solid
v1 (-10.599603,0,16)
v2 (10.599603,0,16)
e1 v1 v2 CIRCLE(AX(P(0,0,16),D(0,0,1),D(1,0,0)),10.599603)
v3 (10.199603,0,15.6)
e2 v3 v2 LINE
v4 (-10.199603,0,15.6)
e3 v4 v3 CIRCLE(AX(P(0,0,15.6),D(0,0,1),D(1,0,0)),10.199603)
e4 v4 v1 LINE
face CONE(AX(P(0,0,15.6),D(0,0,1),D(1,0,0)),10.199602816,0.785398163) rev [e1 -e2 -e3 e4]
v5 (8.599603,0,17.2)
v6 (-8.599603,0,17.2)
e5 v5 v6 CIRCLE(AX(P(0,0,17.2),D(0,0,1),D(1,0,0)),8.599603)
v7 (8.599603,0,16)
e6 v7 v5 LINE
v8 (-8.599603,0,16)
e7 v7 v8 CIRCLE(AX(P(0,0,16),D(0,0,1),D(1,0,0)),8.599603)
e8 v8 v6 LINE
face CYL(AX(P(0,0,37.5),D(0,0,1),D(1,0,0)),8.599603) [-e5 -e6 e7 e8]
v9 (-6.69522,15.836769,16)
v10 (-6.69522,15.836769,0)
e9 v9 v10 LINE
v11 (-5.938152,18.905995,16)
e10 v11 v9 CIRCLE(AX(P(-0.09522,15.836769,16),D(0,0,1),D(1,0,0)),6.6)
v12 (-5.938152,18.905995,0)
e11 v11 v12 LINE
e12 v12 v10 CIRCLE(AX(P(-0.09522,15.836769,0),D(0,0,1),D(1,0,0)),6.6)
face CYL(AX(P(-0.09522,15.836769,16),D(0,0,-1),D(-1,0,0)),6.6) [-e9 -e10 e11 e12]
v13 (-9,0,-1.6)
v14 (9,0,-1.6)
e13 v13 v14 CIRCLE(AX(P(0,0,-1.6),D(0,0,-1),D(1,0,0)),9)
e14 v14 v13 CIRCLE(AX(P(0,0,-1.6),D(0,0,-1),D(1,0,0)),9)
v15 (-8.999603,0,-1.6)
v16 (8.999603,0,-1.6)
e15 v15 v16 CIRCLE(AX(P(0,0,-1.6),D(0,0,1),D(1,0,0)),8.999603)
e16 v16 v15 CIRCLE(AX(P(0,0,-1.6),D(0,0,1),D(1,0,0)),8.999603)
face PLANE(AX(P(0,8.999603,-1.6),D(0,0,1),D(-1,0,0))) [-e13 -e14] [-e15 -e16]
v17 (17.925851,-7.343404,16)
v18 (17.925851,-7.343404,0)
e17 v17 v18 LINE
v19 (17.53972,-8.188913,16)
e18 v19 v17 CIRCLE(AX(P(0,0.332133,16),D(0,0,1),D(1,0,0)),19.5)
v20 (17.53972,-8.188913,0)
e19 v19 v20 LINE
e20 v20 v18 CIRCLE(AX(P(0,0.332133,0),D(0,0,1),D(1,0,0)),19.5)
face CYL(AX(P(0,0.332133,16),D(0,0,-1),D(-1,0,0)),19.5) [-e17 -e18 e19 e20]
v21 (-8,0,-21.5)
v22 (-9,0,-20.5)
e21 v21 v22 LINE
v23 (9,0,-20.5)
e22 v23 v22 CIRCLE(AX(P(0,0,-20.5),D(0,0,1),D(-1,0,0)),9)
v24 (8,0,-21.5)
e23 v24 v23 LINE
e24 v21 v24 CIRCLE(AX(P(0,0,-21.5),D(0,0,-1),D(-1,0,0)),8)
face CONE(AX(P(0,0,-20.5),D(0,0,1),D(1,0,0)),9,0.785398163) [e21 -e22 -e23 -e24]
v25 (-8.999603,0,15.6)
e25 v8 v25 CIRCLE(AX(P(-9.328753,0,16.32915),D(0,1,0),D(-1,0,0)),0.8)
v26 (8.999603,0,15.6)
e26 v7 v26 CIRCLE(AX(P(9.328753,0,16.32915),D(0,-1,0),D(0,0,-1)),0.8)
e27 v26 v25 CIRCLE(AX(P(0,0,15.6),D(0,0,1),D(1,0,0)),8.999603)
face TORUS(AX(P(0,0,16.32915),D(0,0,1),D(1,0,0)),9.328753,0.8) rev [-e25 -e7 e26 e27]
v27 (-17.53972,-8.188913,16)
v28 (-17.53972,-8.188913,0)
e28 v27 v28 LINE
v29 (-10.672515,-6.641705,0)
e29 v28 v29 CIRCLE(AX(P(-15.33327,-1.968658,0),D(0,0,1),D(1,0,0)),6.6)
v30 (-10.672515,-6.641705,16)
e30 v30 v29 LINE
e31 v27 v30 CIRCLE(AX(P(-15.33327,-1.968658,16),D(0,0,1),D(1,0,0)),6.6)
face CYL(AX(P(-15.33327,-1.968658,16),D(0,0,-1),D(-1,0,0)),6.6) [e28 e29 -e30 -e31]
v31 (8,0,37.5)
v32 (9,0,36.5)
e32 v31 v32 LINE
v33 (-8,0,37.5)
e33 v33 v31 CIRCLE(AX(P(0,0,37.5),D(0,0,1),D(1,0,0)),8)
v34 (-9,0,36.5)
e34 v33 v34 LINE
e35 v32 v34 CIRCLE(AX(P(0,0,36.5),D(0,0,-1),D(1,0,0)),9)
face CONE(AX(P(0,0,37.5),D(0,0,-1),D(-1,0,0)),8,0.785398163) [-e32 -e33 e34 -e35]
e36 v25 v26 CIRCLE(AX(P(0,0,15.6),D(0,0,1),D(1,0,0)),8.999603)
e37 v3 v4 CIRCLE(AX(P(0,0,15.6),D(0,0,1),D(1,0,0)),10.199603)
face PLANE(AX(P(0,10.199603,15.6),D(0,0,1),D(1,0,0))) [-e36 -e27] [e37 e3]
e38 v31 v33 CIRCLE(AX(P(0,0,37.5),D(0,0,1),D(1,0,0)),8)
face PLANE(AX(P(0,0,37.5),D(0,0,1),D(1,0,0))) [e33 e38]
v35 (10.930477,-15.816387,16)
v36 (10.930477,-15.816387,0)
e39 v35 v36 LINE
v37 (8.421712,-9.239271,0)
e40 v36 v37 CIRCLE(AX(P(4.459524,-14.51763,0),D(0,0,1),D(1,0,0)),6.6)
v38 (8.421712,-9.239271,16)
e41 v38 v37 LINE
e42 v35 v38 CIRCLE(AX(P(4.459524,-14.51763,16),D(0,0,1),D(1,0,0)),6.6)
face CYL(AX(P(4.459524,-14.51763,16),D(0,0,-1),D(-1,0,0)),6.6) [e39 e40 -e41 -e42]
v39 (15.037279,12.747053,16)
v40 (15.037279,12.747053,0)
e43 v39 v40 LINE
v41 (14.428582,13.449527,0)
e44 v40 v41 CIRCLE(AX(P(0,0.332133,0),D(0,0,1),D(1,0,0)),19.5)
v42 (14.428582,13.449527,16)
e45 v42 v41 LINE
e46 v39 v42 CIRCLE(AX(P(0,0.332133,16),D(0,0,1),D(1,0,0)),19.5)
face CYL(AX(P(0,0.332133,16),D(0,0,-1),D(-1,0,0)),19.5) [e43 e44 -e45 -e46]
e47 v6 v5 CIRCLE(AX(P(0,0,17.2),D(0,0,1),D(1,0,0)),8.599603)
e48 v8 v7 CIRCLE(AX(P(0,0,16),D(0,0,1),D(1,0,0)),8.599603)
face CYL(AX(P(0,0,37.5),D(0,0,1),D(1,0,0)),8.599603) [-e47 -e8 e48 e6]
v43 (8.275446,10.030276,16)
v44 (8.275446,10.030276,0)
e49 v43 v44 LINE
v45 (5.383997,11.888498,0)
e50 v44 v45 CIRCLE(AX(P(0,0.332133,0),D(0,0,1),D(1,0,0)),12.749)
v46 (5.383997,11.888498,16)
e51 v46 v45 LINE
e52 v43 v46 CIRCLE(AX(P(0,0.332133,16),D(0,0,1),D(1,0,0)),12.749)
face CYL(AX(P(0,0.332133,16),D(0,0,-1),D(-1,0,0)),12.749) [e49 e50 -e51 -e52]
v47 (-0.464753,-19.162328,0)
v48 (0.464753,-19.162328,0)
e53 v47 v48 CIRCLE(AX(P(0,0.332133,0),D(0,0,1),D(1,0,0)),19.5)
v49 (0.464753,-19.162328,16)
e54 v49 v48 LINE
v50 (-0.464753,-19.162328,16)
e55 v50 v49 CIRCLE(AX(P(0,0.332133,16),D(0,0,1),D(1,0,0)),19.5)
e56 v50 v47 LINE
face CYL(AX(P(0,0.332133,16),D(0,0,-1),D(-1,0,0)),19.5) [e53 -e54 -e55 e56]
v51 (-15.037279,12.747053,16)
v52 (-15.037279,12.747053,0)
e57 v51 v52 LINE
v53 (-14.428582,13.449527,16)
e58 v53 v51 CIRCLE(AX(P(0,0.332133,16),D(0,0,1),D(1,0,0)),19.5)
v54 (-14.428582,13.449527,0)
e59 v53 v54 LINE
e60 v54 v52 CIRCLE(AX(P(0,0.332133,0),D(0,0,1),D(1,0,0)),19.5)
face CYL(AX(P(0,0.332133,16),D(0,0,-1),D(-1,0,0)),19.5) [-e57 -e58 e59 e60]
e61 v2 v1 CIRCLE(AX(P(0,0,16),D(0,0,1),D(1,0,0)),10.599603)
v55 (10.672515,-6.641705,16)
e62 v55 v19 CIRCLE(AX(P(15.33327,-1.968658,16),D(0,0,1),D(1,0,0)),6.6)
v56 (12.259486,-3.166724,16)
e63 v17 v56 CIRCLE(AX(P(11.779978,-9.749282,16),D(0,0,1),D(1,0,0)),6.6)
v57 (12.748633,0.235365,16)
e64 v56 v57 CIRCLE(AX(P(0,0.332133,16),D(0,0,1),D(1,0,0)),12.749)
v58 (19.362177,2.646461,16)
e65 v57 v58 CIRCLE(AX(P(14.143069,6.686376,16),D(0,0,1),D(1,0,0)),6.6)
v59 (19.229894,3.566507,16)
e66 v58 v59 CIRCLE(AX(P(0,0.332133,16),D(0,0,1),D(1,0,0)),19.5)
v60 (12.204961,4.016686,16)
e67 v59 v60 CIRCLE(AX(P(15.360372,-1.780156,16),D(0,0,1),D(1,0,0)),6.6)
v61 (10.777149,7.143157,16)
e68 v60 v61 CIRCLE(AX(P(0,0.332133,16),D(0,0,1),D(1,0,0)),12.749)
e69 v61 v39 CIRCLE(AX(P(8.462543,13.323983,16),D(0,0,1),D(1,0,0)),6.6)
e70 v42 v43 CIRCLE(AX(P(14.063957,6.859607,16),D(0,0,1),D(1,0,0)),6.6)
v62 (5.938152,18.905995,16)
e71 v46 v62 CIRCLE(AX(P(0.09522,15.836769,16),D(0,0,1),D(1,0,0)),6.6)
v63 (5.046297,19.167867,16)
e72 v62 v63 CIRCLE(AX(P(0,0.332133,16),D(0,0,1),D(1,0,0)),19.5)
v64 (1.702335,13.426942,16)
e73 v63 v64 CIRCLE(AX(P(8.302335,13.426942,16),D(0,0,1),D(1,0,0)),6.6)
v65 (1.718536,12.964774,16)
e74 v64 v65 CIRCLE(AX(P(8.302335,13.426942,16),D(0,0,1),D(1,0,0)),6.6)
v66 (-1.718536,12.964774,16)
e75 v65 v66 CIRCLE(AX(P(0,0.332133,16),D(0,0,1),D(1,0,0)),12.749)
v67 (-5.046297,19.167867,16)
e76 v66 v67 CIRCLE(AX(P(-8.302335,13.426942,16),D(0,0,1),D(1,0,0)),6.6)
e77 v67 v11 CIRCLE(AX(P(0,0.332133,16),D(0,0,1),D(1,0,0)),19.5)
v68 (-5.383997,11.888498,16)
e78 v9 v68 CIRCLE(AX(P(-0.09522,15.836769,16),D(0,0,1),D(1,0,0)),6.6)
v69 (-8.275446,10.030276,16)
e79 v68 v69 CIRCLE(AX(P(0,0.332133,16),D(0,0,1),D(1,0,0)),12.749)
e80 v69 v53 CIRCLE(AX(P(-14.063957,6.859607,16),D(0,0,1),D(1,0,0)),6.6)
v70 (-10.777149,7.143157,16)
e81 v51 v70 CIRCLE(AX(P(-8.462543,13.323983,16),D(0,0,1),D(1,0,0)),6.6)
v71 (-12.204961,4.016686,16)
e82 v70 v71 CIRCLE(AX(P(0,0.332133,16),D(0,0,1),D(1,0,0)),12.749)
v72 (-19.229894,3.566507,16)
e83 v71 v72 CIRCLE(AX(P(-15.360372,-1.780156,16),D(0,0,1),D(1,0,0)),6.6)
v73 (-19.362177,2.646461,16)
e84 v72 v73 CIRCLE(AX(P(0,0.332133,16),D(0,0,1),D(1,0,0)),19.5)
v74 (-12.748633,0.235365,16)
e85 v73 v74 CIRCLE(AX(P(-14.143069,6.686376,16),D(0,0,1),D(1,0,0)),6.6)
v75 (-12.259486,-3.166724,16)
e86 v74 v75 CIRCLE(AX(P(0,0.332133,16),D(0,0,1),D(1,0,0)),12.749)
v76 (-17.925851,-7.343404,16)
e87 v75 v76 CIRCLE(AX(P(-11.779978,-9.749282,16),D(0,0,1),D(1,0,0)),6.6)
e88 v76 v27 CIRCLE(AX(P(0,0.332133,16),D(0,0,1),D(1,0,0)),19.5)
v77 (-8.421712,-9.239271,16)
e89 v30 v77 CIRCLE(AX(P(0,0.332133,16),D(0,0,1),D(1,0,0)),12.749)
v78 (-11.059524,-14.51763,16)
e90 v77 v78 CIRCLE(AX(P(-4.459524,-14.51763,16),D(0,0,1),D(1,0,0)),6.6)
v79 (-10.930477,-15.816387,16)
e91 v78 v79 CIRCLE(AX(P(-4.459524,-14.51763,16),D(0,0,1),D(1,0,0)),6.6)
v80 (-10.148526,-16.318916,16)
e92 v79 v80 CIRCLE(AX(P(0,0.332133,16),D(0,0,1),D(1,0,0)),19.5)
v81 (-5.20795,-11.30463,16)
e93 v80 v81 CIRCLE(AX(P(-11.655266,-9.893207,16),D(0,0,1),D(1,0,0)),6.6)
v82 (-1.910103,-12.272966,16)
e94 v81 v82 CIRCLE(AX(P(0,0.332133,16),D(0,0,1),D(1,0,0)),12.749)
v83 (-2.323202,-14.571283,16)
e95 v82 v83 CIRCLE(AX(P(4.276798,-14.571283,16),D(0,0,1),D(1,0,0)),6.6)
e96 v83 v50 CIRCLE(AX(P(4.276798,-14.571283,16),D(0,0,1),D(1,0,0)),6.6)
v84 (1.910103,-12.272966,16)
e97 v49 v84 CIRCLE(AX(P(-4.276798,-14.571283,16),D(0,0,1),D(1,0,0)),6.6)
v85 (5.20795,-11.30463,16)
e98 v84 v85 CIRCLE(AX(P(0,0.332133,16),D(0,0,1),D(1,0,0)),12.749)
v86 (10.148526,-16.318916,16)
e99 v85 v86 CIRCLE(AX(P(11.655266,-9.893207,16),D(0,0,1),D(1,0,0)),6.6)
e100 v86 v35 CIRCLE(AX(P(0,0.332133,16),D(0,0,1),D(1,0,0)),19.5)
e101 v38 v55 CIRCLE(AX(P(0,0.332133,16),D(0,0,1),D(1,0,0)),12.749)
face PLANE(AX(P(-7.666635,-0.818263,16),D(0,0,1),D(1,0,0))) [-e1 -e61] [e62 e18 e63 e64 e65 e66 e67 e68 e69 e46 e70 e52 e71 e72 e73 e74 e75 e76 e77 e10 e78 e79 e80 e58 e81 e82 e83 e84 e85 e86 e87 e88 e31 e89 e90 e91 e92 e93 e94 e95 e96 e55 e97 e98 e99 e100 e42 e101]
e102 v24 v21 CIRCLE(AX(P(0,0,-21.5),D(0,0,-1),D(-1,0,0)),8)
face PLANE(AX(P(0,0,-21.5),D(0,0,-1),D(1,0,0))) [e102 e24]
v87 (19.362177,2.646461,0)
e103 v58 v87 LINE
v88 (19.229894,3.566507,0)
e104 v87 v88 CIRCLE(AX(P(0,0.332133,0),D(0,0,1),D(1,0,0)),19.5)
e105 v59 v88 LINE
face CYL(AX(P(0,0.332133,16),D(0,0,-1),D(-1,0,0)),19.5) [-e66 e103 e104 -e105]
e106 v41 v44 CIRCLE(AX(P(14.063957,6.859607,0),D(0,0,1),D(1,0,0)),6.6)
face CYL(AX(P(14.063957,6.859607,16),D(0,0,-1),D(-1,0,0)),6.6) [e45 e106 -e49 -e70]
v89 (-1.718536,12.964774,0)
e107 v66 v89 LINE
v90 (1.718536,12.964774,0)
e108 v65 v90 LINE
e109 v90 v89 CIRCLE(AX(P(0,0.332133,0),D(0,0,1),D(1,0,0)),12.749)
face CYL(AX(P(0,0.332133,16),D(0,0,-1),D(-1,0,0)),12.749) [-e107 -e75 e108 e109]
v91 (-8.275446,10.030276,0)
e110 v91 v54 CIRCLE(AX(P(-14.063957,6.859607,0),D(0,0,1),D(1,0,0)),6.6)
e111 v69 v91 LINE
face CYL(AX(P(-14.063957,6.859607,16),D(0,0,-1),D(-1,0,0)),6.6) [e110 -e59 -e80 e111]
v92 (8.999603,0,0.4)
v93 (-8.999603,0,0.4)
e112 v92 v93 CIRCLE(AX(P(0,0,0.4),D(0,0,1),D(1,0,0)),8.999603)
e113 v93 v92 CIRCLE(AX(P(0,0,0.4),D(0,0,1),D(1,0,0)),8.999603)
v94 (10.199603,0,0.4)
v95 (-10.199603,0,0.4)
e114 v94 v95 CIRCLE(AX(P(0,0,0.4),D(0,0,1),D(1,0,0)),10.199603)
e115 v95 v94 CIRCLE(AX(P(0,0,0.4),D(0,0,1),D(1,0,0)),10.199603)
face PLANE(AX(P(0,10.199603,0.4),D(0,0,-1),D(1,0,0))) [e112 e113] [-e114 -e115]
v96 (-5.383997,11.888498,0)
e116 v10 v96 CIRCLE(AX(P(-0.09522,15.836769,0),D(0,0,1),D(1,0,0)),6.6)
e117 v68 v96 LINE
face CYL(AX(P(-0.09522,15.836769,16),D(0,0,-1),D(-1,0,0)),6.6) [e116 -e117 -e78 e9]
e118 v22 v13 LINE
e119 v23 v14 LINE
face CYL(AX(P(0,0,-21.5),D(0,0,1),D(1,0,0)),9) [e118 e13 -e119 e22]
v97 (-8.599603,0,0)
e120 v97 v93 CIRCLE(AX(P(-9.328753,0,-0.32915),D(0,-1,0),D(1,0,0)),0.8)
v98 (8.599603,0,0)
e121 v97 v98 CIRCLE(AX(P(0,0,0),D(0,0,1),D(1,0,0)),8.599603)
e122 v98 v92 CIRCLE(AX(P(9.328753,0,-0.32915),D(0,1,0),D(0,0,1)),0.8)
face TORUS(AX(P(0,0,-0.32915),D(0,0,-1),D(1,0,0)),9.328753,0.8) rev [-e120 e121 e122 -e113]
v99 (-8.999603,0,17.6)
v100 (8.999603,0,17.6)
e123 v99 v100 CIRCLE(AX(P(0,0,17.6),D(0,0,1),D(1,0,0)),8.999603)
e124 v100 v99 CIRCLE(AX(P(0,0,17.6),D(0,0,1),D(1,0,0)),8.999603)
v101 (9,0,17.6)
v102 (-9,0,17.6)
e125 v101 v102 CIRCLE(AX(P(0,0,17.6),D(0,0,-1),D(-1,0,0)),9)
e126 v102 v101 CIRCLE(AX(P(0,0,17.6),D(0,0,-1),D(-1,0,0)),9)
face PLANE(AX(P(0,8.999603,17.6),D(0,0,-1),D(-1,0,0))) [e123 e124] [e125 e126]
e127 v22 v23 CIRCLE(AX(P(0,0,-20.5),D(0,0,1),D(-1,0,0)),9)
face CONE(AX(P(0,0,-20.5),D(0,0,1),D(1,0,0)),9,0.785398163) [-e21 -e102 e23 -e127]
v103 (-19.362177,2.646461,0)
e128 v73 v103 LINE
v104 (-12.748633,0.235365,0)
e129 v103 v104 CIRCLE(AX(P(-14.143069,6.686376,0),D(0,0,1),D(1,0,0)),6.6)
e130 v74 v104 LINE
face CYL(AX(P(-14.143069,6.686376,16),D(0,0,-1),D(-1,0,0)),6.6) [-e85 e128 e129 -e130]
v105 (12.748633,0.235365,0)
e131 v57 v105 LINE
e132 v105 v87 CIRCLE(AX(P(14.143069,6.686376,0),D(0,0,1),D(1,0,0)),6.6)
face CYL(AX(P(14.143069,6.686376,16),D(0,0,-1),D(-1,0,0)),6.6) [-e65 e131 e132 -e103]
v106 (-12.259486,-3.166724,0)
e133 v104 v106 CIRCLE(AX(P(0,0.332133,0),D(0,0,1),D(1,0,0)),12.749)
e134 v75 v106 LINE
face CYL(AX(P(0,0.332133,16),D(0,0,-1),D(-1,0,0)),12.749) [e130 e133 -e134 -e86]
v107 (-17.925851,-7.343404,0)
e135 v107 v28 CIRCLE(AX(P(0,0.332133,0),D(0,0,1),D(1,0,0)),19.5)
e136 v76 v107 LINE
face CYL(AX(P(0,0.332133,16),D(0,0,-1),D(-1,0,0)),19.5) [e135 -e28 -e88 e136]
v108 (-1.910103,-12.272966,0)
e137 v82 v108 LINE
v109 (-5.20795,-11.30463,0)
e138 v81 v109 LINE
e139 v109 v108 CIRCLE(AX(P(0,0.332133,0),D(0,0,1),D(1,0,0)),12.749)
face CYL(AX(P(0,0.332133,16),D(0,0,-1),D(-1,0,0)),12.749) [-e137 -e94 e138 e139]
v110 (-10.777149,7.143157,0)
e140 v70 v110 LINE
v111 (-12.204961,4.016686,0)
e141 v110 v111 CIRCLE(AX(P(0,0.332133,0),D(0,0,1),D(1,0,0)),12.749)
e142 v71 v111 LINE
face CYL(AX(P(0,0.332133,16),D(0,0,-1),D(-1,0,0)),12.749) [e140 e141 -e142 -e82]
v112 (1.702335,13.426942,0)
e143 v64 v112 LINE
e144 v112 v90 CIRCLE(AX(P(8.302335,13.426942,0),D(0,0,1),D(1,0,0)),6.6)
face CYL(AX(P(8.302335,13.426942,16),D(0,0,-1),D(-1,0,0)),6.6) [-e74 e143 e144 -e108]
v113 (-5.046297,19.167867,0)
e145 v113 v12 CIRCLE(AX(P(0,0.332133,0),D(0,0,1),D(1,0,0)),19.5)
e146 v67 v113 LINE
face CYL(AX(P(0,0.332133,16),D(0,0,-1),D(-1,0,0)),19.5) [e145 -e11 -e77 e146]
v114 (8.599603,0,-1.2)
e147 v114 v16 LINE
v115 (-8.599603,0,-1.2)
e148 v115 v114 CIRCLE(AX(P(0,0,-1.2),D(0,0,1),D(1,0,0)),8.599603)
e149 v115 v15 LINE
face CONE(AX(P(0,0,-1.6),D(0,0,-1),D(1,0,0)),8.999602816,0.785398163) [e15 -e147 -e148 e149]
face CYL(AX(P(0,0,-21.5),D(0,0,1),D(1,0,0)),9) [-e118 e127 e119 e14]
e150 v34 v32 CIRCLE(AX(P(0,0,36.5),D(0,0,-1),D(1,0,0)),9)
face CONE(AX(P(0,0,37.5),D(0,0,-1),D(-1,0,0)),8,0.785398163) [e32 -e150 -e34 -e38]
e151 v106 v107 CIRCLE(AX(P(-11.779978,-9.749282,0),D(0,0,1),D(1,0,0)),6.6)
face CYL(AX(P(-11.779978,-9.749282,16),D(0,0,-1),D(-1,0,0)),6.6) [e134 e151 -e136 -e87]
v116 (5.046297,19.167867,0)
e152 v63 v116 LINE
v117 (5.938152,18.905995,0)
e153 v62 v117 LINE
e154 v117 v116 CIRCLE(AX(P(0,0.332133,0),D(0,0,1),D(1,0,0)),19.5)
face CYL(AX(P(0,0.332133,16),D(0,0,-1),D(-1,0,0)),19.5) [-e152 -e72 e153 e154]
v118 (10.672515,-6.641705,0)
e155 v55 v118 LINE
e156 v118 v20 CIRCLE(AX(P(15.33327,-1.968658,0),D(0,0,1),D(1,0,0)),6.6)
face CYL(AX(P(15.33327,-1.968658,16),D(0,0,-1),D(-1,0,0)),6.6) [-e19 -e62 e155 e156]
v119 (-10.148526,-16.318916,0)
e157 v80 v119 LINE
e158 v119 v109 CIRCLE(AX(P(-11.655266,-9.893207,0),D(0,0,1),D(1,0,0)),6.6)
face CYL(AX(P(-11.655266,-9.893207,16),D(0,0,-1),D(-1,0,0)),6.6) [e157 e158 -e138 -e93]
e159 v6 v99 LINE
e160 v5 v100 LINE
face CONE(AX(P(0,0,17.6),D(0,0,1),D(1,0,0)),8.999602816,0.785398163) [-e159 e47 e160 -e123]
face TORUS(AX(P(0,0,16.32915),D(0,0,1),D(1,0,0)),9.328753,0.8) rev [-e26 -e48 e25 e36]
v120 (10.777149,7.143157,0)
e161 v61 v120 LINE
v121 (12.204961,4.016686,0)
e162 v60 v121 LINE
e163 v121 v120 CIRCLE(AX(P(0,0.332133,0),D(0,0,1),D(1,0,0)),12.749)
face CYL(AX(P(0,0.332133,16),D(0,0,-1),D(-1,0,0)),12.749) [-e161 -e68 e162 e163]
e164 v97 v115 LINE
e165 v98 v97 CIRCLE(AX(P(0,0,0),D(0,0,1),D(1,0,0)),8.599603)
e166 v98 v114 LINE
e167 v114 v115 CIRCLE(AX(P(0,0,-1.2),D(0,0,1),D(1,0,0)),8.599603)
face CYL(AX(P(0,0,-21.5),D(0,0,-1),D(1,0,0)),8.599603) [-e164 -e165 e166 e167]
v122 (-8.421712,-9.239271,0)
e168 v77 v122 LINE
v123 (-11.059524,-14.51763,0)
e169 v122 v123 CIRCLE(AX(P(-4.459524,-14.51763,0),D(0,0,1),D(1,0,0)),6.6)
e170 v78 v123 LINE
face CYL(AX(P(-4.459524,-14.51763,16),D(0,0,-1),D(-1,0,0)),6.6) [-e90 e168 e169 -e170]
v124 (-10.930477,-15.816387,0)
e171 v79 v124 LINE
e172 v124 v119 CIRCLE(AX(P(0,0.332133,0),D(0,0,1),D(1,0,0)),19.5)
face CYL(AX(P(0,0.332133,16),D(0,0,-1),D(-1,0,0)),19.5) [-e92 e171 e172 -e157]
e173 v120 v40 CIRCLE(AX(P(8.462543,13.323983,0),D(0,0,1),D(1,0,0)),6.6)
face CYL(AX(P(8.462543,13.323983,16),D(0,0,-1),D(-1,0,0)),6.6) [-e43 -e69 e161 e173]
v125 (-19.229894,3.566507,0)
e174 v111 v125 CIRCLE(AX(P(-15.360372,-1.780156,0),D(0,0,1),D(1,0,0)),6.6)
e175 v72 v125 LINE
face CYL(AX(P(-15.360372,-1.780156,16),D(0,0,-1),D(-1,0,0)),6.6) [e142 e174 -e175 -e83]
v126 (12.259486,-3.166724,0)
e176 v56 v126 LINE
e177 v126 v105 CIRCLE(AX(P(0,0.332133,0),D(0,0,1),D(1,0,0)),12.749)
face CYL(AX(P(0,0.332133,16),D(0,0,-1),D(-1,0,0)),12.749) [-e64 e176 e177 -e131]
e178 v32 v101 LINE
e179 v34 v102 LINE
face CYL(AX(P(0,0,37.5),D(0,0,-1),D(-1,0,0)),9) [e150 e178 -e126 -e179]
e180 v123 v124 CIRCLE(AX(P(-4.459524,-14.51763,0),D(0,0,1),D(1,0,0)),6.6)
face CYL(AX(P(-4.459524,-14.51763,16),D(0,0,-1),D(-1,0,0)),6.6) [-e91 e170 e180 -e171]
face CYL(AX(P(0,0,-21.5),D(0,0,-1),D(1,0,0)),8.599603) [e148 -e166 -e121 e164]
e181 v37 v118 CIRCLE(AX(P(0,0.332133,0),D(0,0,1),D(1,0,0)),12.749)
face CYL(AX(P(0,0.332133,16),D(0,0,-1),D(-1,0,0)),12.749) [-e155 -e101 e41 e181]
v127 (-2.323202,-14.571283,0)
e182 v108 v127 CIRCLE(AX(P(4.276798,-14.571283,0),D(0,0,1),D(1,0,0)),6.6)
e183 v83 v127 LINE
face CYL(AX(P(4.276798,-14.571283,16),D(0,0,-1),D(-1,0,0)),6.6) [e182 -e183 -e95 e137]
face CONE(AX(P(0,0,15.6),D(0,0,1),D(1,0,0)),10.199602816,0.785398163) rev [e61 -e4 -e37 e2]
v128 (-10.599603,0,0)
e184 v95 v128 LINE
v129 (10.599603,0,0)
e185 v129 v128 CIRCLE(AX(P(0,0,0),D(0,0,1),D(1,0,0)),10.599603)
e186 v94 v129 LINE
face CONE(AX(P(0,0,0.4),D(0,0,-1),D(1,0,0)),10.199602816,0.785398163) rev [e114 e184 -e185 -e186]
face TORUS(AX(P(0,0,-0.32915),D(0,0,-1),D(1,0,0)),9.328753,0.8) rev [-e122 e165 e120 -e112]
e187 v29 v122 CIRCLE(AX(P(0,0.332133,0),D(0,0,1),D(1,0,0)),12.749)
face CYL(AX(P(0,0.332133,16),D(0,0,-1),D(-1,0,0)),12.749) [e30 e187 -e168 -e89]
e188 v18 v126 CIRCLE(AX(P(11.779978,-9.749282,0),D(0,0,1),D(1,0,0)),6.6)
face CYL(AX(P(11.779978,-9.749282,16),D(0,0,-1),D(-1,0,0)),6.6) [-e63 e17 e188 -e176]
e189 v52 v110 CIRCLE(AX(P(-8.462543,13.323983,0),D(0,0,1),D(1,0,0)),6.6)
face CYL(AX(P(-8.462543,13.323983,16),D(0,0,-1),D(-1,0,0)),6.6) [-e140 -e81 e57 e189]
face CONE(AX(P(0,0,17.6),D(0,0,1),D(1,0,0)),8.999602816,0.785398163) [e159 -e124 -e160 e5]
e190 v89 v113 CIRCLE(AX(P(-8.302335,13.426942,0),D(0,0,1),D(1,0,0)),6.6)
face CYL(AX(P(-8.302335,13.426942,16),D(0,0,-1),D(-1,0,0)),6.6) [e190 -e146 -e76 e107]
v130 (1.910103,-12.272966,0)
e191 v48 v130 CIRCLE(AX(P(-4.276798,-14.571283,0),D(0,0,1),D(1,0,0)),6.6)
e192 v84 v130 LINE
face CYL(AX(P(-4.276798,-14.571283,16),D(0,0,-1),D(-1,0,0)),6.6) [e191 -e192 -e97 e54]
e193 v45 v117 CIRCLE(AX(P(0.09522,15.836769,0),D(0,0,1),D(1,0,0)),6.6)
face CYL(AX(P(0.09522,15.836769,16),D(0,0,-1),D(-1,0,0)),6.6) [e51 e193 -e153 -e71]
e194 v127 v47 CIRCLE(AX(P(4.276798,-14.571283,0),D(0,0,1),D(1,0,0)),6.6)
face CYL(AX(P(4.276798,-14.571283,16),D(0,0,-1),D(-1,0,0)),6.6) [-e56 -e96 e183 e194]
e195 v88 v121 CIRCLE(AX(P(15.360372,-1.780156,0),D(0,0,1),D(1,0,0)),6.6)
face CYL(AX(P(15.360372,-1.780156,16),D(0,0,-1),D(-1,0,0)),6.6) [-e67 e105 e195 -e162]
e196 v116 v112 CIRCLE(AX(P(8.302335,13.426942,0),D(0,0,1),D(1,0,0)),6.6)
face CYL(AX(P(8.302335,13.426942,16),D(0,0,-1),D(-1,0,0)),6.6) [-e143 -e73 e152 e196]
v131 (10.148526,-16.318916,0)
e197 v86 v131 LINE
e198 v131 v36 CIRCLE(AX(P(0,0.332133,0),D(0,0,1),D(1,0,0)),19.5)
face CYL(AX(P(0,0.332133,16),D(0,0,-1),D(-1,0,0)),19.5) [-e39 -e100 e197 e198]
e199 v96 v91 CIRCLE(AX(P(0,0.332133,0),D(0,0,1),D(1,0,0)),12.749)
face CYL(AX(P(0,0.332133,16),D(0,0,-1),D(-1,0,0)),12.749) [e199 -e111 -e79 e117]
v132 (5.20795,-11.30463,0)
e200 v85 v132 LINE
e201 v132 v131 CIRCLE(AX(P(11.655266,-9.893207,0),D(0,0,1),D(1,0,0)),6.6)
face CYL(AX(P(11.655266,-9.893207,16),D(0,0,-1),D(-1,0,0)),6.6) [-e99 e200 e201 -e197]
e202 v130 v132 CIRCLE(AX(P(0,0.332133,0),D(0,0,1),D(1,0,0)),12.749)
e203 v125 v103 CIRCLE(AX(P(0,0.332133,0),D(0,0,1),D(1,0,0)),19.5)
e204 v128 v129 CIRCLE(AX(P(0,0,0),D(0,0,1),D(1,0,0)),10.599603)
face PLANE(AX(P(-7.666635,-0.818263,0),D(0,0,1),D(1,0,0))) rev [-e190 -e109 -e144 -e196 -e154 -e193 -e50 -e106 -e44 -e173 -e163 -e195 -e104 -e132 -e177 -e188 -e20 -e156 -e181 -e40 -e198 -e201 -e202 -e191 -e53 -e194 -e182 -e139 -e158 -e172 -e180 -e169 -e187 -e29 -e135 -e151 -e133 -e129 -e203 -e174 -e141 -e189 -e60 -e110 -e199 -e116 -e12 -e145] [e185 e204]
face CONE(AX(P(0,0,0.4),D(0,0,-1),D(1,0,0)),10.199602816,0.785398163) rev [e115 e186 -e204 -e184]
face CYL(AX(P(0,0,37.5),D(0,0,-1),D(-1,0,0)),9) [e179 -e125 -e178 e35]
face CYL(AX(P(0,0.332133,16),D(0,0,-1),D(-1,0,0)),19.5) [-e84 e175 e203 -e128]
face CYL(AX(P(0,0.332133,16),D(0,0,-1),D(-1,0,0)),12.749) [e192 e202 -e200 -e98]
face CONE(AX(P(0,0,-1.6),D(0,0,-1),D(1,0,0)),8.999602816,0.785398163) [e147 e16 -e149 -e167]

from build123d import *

# Parameters (mm, degrees)
EXTRUDE_1_DEPTH = 16
SKETCH_3_R      = 9
EXTRUDE_2_DEPTH = 21.5
CHAMFER_1_SIZE  = 1


with BuildPart() as part:
    # 草图2 → 凸台-拉伸1 (new body)
    with BuildSketch(Plane.XY):
        with BuildLine():
            ThreePointArc((-17.539719795, -8.188913461), (-13.882626521, -8.407262966), (-10.672515451, -6.641705083))
            ThreePointArc((-10.672515451, -6.641705083), (-9.635051323, -8.016686689), (-8.421711588, -9.239271212))
            ThreePointArc((-8.421711588, -9.239271212), (-10.626145075, -12.165442895), (-10.930476691, -15.816386607))
            ThreePointArc((-10.930476691, -15.816386607), (-10.54249594, -16.072311082), (-10.148525822, -16.318915917))
            ThreePointArc((-10.148525822, -16.318915917), (-6.95393453, -14.525429313), (-5.207949909, -11.304630433))
            ThreePointArc((-5.207949909, -11.304630433), (-3.591808367, -11.900443112), (-1.910102932, -12.272965675))
            ThreePointArc((-1.910102932, -12.272965675), (-2.18258254, -15.926424664), (-0.464753394, -19.162328053))
            ThreePointArc((-0.464753394, -19.162328053), (0, -19.167867192), (0.464753394, -19.162328053))
            ThreePointArc((0.464753394, -19.162328053), (2.18258254, -15.926424664), (1.910102932, -12.272965675))
            ThreePointArc((1.910102932, -12.272965675), (3.591808367, -11.900443112), (5.207949909, -11.304630433))
            ThreePointArc((5.207949909, -11.304630433), (6.95393453, -14.525429313), (10.148525822, -16.318915917))
            ThreePointArc((10.148525822, -16.318915917), (10.54249594, -16.072311082), (10.930476691, -15.816386607))
            ThreePointArc((10.930476691, -15.816386607), (10.626145075, -12.165442895), (8.421711588, -9.239271212))
            ThreePointArc((8.421711588, -9.239271212), (9.635051323, -8.016686689), (10.672515451, -6.641705083))
            ThreePointArc((10.672515451, -6.641705083), (13.882626521, -8.407262966), (17.539719795, -8.188913461))
            ThreePointArc((17.539719795, -8.188913461), (17.737823909, -7.768459945), (17.925850869, -7.343404347))
            ThreePointArc((17.925850869, -7.343404347), (15.69598163, -4.436569144), (12.25948632, -3.166723601))
            ThreePointArc((12.25948632, -3.166723601), (12.619233563, -1.482239065), (12.748632746, 0.235364522))
            ThreePointArc((12.748632746, 0.235364522), (16.403682682, 0.485599789), (19.362176663, 2.646460979))
            ThreePointArc((19.362176663, 2.646460979), (19.301518117, 3.107272155), (19.229894055, 3.566506728))
            ThreePointArc((19.229894055, 3.566506728), (15.782454919, 4.806333783), (12.204960767, 4.016686199))
            ThreePointArc((12.204960767, 4.016686199), (11.596898309, 5.628258809), (10.777149222, 7.143157375))
            ThreePointArc((10.777149222, 7.143157375), (13.716685494, 9.329737862), (15.037279247, 12.747052577))
            ThreePointArc((15.037279247, 12.747052577), (14.7371167, 13.10191712), (14.42858175, 13.449526936))
            ThreePointArc((14.42858175, 13.449526936), (10.858110285, 12.628709513), (8.275446406, 10.030276331))
            ThreePointArc((8.275446406, 10.030276331), (6.892629782, 11.057274099), (5.383996967, 11.888498053))
            ThreePointArc((5.383996967, 11.888498053), (6.674737579, 15.317199905), (5.938151919, 18.905994868))
            ThreePointArc((5.938151919, 18.905994868), (5.493784858, 19.042245794), (5.046296687, 19.167867192))
            ThreePointArc((5.046296687, 19.167867192), (2.486392356, 16.547009024), (1.718536283, 12.964774418))
            ThreePointArc((1.718536283, 12.964774418), (0, 13.081132808), (-1.718536283, 12.964774418))
            ThreePointArc((-1.718536283, 12.964774418), (-2.486392356, 16.547009024), (-5.046296687, 19.167867192))
            ThreePointArc((-5.046296687, 19.167867192), (-5.493784858, 19.042245794), (-5.938151919, 18.905994868))
            ThreePointArc((-5.938151919, 18.905994868), (-6.674737579, 15.317199905), (-5.383996967, 11.888498053))
            ThreePointArc((-5.383996967, 11.888498053), (-6.892629782, 11.057274099), (-8.275446406, 10.030276331))
            ThreePointArc((-8.275446406, 10.030276331), (-10.858110285, 12.628709513), (-14.42858175, 13.449526936))
            ThreePointArc((-14.42858175, 13.449526936), (-14.7371167, 13.10191712), (-15.037279247, 12.747052577))
            ThreePointArc((-15.037279247, 12.747052577), (-13.716685494, 9.329737862), (-10.777149222, 7.143157375))
            ThreePointArc((-10.777149222, 7.143157375), (-11.596898309, 5.628258809), (-12.204960767, 4.016686199))
            ThreePointArc((-12.204960767, 4.016686199), (-15.782454919, 4.806333783), (-19.229894055, 3.566506728))
            ThreePointArc((-19.229894055, 3.566506728), (-19.301518117, 3.107272155), (-19.362176663, 2.646460979))
            ThreePointArc((-19.362176663, 2.646460979), (-16.403682682, 0.485599789), (-12.748632746, 0.235364522))
            ThreePointArc((-12.748632746, 0.235364522), (-12.619233563, -1.482239065), (-12.25948632, -3.166723601))
            ThreePointArc((-12.25948632, -3.166723601), (-15.69598163, -4.436569144), (-17.925850869, -7.343404347))
            ThreePointArc((-17.925850869, -7.343404347), (-17.737823909, -7.768459945), (-17.539719795, -8.188913461))
        make_face()
    extrude(amount=EXTRUDE_1_DEPTH)

    # 草图3 → 凸台-拉伸2 (add)
    with BuildSketch(Plane.XY.offset(16)):
        Circle(SKETCH_3_R)
    extrude_2 = extrude(amount=EXTRUDE_2_DEPTH)

    # 草图4 → 切除-旋转1 (revolve, cut)
    with BuildSketch(Plane(origin=(0, 0, 0), x_dir=(0, 0, -1), z_dir=(1, 0, 0)), mode=Mode.PRIVATE) as cut_revolve_1_sk:
        with BuildLine():
            Line((-17.6, 8.999602816), (-17.2, 8.599602816))
            Line((-17.2, 8.599602816), (-16, 8.599602816))
            ThreePointArc((-16, 8.599602816), (-15.763464837, 8.763067654), (-15.6, 8.999602816))
            Line((-15.6, 8.999602816), (-15.6, 10.199602816))
            Line((-15.6, 10.199602816), (-16, 10.599602816))
            Line((-16, 10.599602816), (-17.6, 10.599602816))
            Line((-17.6, 10.599602816), (-17.6, 8.999602816))
        make_face()
    cut_revolve_1 = revolve(cut_revolve_1_sk.sketch.rotate(Axis((0, 0, 37.5), (0, 0, -1)), 90), axis=Axis((0, 0, 37.5), (0, 0, -1)), mode=Mode.SUBTRACT)

    # 镜向1: 凸台-拉伸2, 切除-旋转1 across plane
    add(extrude_2.mirror(Plane.XY.offset(8)))
    add(cut_revolve_1.mirror(Plane.XY.offset(8)), mode=Mode.SUBTRACT)

    # 倒角1
    chamfer_1_edges = [part.edges().sort_by_distance(p)[0] for p in [
        (-9, 0, 37.5),
        (-9, 0, -21.5),
    ]]
    chamfer(chamfer_1_edges, length=CHAMFER_1_SIZE)


solid = part.part
